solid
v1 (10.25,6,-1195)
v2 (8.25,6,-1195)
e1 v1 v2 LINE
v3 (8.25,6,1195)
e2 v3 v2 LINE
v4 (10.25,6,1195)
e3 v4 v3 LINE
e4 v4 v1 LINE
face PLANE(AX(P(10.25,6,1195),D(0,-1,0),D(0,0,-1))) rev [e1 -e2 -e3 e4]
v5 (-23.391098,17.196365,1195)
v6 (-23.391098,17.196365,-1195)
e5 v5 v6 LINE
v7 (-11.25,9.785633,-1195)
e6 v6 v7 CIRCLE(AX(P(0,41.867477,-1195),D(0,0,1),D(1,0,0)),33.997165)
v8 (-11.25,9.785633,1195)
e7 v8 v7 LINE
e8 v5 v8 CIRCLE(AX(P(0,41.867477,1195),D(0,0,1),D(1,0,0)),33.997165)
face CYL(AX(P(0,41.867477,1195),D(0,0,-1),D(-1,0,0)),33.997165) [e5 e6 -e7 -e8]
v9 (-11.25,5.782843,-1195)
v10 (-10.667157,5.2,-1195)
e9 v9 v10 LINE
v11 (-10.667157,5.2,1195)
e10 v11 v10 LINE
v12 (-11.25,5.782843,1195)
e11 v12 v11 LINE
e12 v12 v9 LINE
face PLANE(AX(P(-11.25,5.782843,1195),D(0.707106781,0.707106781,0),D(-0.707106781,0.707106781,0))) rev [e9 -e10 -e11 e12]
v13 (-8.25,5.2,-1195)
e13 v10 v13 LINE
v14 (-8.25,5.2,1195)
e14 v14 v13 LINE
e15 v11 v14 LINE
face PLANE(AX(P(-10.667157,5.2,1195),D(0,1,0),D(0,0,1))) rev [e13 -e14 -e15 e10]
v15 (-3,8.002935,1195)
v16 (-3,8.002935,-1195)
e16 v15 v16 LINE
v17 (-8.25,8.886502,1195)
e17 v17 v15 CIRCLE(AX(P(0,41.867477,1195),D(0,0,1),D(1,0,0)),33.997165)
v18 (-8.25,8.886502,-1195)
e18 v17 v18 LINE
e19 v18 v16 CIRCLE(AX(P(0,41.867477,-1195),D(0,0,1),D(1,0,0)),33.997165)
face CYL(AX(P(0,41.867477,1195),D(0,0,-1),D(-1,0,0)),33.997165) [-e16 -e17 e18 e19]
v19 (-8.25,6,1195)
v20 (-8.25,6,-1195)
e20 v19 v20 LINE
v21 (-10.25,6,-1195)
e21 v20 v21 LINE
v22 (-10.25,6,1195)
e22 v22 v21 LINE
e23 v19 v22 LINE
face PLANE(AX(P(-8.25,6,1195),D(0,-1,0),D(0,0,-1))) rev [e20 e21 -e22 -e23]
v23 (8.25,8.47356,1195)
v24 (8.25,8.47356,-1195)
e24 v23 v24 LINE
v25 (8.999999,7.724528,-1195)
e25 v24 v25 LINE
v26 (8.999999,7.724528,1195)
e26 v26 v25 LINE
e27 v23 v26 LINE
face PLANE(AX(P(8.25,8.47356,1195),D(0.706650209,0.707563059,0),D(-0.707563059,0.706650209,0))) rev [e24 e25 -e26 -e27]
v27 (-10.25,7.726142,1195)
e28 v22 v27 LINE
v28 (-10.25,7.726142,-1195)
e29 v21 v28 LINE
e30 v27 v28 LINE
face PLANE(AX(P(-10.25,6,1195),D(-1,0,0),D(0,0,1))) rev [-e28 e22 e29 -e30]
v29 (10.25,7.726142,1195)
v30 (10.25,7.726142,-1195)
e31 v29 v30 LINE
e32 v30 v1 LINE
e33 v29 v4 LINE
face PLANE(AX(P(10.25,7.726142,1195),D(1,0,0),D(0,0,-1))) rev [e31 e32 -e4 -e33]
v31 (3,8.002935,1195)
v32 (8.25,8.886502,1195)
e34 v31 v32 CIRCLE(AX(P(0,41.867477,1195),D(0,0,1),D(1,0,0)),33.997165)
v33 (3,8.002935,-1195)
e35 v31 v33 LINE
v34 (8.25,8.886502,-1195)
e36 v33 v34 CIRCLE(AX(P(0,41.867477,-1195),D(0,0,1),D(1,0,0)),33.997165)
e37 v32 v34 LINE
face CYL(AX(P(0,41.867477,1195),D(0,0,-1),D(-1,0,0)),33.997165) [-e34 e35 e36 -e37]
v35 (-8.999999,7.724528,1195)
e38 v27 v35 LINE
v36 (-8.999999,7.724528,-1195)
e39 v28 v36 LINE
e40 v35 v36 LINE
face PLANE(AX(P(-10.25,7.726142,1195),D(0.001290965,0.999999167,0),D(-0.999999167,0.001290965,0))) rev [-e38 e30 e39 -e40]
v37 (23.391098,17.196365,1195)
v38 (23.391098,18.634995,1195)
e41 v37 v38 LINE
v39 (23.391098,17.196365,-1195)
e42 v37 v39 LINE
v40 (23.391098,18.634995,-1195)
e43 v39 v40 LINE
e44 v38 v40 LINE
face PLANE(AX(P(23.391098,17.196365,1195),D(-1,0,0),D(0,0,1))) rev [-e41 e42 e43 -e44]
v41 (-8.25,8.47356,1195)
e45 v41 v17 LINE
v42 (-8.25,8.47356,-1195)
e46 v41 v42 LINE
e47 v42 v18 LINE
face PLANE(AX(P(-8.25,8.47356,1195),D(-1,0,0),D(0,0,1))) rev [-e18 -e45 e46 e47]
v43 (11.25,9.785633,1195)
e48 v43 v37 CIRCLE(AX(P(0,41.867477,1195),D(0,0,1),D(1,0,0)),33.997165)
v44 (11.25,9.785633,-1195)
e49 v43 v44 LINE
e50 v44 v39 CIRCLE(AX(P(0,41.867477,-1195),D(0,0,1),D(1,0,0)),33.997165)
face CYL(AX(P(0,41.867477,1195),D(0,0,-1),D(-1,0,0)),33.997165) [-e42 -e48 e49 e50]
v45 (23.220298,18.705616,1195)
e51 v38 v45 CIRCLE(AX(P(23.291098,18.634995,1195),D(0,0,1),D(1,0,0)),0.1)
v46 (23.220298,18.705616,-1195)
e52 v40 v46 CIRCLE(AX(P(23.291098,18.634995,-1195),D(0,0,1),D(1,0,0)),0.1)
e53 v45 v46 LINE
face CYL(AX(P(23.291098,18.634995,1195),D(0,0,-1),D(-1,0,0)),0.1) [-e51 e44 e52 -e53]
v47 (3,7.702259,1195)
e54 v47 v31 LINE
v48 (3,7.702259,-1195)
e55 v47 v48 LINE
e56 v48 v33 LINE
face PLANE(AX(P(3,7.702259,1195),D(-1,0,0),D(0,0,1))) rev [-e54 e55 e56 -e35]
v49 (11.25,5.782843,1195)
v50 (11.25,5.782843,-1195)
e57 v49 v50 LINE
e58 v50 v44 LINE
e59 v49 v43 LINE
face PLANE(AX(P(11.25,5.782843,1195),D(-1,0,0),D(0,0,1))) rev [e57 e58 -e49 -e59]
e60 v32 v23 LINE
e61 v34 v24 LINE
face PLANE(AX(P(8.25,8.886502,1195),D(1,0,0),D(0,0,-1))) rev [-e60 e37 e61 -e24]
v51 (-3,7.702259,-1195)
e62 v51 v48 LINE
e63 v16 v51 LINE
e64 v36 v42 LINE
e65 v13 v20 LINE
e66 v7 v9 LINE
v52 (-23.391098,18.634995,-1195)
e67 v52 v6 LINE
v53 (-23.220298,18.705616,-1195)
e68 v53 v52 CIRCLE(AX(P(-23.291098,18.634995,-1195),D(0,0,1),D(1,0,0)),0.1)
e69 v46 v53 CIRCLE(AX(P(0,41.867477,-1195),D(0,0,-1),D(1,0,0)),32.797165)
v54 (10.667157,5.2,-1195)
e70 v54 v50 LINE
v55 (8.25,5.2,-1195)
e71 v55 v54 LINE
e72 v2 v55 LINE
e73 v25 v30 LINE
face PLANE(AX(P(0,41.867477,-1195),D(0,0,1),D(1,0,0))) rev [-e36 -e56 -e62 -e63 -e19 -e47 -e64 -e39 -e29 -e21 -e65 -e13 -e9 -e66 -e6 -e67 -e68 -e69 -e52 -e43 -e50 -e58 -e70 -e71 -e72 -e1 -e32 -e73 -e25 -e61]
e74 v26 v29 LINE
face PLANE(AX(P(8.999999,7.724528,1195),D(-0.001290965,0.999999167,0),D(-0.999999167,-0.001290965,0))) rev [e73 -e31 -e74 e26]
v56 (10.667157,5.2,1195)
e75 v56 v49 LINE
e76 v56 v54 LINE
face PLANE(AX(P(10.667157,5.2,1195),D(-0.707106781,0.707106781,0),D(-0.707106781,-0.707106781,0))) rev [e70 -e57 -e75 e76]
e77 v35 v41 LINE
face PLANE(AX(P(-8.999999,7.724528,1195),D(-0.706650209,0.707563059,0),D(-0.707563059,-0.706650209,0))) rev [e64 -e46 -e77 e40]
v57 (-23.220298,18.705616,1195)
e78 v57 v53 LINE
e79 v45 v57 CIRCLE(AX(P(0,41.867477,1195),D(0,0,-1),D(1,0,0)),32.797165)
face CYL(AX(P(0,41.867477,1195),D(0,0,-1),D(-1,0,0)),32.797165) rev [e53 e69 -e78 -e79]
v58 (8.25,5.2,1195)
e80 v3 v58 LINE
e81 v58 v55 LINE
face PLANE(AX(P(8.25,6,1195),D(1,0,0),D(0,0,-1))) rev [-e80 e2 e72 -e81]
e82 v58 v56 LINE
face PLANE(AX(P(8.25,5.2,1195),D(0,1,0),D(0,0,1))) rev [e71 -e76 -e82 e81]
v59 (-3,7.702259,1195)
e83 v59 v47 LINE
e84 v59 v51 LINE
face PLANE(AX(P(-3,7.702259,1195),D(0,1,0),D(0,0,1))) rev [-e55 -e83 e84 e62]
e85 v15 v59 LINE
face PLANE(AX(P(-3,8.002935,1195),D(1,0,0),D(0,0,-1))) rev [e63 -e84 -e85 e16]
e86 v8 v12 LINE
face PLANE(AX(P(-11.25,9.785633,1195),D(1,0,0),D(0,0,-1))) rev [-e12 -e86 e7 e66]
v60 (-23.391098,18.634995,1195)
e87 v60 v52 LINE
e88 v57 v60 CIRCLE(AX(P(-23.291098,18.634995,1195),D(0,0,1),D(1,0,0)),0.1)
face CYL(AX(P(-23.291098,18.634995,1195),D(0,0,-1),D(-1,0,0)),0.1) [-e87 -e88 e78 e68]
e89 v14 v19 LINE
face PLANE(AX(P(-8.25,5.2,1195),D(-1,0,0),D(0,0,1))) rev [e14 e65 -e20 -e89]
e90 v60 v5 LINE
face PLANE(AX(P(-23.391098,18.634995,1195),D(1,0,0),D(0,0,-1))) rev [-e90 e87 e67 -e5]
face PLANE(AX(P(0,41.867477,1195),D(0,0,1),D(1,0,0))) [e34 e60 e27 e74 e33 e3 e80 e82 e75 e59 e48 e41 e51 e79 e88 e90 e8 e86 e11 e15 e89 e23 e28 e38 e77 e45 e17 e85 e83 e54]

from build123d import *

# Parameters (mm, degrees)
EXTRUDE_1_DEPTH = 1195


with BuildPart() as part:
    # 草图2 → 凸台-拉伸1 (new, symmetric)
    with BuildSketch(Plane.XY):
        with BuildLine():
            Line((-11.25, 5.782842712), (-10.667157288, 5.199999999))
            Line((-10.667157288, 5.199999999), (-8.25, 5.199999999))
            Line((-8.25, 5.199999999), (-8.25, 6))
            Line((-8.25, 6), (-10.25, 6))
            Line((-10.25, 6), (-10.25, 7.726142057))
            Line((-10.25, 7.726142057), (-8.999999375, 7.724528349))
            Line((-8.999999375, 7.724528349), (-8.25, 8.473560125))
            Line((-8.25, 8.473560125), (-8.25, 8.88650173))
            ThreePointArc((-8.25, 8.88650173), (-5.642322013, 8.341793831), (-3, 8.002934636))
            Line((-3, 8.002934636), (-3, 7.70225919))
            Line((-3, 7.70225919), (3, 7.70225919))
            Line((3, 7.70225919), (3, 8.002934636))
            ThreePointArc((3, 8.002934636), (5.642322013, 8.341793831), (8.25, 8.88650173))
            Line((8.25, 8.88650173), (8.25, 8.473560125))
            Line((8.25, 8.473560125), (8.999999375, 7.724528349))
            Line((8.999999375, 7.724528349), (10.25, 7.726142057))
            Line((10.25, 7.726142057), (10.25, 6))
            Line((10.25, 6), (8.25, 6))
            Line((8.25, 6), (8.25, 5.2))
            Line((8.25, 5.2), (10.667157288, 5.2))
            Line((10.667157288, 5.2), (11.25, 5.782842712))
            Line((11.25, 5.782842712), (11.25, 9.785632758))
            ThreePointArc((11.25, 9.785632758), (17.712457567, 12.84892987), (23.391097866, 17.196364903))
            Line((23.391097866, 17.196364903), (23.391097866, 18.63499481))
            ThreePointArc((23.391097866, 18.63499481), (23.329308001, 18.727406852), (23.220298155, 18.705616343))
            ThreePointArc((23.220298155, 18.705616343), (0, 9.070311977), (-23.220298155, 18.705616342))
            ThreePointArc((-23.220298155, 18.705616342), (-23.329308002, 18.727406852), (-23.391097866, 18.634994809))
            Line((-23.391097866, 18.634994809), (-23.391097866, 17.196364902))
            ThreePointArc((-23.391097866, 17.196364902), (-17.712457568, 12.84892987), (-11.25, 9.785632758))
            Line((-11.25, 9.785632758), (-11.25, 5.782842712))
        make_face()
    extrude(amount=EXTRUDE_1_DEPTH, both=True)


solid = part.part
